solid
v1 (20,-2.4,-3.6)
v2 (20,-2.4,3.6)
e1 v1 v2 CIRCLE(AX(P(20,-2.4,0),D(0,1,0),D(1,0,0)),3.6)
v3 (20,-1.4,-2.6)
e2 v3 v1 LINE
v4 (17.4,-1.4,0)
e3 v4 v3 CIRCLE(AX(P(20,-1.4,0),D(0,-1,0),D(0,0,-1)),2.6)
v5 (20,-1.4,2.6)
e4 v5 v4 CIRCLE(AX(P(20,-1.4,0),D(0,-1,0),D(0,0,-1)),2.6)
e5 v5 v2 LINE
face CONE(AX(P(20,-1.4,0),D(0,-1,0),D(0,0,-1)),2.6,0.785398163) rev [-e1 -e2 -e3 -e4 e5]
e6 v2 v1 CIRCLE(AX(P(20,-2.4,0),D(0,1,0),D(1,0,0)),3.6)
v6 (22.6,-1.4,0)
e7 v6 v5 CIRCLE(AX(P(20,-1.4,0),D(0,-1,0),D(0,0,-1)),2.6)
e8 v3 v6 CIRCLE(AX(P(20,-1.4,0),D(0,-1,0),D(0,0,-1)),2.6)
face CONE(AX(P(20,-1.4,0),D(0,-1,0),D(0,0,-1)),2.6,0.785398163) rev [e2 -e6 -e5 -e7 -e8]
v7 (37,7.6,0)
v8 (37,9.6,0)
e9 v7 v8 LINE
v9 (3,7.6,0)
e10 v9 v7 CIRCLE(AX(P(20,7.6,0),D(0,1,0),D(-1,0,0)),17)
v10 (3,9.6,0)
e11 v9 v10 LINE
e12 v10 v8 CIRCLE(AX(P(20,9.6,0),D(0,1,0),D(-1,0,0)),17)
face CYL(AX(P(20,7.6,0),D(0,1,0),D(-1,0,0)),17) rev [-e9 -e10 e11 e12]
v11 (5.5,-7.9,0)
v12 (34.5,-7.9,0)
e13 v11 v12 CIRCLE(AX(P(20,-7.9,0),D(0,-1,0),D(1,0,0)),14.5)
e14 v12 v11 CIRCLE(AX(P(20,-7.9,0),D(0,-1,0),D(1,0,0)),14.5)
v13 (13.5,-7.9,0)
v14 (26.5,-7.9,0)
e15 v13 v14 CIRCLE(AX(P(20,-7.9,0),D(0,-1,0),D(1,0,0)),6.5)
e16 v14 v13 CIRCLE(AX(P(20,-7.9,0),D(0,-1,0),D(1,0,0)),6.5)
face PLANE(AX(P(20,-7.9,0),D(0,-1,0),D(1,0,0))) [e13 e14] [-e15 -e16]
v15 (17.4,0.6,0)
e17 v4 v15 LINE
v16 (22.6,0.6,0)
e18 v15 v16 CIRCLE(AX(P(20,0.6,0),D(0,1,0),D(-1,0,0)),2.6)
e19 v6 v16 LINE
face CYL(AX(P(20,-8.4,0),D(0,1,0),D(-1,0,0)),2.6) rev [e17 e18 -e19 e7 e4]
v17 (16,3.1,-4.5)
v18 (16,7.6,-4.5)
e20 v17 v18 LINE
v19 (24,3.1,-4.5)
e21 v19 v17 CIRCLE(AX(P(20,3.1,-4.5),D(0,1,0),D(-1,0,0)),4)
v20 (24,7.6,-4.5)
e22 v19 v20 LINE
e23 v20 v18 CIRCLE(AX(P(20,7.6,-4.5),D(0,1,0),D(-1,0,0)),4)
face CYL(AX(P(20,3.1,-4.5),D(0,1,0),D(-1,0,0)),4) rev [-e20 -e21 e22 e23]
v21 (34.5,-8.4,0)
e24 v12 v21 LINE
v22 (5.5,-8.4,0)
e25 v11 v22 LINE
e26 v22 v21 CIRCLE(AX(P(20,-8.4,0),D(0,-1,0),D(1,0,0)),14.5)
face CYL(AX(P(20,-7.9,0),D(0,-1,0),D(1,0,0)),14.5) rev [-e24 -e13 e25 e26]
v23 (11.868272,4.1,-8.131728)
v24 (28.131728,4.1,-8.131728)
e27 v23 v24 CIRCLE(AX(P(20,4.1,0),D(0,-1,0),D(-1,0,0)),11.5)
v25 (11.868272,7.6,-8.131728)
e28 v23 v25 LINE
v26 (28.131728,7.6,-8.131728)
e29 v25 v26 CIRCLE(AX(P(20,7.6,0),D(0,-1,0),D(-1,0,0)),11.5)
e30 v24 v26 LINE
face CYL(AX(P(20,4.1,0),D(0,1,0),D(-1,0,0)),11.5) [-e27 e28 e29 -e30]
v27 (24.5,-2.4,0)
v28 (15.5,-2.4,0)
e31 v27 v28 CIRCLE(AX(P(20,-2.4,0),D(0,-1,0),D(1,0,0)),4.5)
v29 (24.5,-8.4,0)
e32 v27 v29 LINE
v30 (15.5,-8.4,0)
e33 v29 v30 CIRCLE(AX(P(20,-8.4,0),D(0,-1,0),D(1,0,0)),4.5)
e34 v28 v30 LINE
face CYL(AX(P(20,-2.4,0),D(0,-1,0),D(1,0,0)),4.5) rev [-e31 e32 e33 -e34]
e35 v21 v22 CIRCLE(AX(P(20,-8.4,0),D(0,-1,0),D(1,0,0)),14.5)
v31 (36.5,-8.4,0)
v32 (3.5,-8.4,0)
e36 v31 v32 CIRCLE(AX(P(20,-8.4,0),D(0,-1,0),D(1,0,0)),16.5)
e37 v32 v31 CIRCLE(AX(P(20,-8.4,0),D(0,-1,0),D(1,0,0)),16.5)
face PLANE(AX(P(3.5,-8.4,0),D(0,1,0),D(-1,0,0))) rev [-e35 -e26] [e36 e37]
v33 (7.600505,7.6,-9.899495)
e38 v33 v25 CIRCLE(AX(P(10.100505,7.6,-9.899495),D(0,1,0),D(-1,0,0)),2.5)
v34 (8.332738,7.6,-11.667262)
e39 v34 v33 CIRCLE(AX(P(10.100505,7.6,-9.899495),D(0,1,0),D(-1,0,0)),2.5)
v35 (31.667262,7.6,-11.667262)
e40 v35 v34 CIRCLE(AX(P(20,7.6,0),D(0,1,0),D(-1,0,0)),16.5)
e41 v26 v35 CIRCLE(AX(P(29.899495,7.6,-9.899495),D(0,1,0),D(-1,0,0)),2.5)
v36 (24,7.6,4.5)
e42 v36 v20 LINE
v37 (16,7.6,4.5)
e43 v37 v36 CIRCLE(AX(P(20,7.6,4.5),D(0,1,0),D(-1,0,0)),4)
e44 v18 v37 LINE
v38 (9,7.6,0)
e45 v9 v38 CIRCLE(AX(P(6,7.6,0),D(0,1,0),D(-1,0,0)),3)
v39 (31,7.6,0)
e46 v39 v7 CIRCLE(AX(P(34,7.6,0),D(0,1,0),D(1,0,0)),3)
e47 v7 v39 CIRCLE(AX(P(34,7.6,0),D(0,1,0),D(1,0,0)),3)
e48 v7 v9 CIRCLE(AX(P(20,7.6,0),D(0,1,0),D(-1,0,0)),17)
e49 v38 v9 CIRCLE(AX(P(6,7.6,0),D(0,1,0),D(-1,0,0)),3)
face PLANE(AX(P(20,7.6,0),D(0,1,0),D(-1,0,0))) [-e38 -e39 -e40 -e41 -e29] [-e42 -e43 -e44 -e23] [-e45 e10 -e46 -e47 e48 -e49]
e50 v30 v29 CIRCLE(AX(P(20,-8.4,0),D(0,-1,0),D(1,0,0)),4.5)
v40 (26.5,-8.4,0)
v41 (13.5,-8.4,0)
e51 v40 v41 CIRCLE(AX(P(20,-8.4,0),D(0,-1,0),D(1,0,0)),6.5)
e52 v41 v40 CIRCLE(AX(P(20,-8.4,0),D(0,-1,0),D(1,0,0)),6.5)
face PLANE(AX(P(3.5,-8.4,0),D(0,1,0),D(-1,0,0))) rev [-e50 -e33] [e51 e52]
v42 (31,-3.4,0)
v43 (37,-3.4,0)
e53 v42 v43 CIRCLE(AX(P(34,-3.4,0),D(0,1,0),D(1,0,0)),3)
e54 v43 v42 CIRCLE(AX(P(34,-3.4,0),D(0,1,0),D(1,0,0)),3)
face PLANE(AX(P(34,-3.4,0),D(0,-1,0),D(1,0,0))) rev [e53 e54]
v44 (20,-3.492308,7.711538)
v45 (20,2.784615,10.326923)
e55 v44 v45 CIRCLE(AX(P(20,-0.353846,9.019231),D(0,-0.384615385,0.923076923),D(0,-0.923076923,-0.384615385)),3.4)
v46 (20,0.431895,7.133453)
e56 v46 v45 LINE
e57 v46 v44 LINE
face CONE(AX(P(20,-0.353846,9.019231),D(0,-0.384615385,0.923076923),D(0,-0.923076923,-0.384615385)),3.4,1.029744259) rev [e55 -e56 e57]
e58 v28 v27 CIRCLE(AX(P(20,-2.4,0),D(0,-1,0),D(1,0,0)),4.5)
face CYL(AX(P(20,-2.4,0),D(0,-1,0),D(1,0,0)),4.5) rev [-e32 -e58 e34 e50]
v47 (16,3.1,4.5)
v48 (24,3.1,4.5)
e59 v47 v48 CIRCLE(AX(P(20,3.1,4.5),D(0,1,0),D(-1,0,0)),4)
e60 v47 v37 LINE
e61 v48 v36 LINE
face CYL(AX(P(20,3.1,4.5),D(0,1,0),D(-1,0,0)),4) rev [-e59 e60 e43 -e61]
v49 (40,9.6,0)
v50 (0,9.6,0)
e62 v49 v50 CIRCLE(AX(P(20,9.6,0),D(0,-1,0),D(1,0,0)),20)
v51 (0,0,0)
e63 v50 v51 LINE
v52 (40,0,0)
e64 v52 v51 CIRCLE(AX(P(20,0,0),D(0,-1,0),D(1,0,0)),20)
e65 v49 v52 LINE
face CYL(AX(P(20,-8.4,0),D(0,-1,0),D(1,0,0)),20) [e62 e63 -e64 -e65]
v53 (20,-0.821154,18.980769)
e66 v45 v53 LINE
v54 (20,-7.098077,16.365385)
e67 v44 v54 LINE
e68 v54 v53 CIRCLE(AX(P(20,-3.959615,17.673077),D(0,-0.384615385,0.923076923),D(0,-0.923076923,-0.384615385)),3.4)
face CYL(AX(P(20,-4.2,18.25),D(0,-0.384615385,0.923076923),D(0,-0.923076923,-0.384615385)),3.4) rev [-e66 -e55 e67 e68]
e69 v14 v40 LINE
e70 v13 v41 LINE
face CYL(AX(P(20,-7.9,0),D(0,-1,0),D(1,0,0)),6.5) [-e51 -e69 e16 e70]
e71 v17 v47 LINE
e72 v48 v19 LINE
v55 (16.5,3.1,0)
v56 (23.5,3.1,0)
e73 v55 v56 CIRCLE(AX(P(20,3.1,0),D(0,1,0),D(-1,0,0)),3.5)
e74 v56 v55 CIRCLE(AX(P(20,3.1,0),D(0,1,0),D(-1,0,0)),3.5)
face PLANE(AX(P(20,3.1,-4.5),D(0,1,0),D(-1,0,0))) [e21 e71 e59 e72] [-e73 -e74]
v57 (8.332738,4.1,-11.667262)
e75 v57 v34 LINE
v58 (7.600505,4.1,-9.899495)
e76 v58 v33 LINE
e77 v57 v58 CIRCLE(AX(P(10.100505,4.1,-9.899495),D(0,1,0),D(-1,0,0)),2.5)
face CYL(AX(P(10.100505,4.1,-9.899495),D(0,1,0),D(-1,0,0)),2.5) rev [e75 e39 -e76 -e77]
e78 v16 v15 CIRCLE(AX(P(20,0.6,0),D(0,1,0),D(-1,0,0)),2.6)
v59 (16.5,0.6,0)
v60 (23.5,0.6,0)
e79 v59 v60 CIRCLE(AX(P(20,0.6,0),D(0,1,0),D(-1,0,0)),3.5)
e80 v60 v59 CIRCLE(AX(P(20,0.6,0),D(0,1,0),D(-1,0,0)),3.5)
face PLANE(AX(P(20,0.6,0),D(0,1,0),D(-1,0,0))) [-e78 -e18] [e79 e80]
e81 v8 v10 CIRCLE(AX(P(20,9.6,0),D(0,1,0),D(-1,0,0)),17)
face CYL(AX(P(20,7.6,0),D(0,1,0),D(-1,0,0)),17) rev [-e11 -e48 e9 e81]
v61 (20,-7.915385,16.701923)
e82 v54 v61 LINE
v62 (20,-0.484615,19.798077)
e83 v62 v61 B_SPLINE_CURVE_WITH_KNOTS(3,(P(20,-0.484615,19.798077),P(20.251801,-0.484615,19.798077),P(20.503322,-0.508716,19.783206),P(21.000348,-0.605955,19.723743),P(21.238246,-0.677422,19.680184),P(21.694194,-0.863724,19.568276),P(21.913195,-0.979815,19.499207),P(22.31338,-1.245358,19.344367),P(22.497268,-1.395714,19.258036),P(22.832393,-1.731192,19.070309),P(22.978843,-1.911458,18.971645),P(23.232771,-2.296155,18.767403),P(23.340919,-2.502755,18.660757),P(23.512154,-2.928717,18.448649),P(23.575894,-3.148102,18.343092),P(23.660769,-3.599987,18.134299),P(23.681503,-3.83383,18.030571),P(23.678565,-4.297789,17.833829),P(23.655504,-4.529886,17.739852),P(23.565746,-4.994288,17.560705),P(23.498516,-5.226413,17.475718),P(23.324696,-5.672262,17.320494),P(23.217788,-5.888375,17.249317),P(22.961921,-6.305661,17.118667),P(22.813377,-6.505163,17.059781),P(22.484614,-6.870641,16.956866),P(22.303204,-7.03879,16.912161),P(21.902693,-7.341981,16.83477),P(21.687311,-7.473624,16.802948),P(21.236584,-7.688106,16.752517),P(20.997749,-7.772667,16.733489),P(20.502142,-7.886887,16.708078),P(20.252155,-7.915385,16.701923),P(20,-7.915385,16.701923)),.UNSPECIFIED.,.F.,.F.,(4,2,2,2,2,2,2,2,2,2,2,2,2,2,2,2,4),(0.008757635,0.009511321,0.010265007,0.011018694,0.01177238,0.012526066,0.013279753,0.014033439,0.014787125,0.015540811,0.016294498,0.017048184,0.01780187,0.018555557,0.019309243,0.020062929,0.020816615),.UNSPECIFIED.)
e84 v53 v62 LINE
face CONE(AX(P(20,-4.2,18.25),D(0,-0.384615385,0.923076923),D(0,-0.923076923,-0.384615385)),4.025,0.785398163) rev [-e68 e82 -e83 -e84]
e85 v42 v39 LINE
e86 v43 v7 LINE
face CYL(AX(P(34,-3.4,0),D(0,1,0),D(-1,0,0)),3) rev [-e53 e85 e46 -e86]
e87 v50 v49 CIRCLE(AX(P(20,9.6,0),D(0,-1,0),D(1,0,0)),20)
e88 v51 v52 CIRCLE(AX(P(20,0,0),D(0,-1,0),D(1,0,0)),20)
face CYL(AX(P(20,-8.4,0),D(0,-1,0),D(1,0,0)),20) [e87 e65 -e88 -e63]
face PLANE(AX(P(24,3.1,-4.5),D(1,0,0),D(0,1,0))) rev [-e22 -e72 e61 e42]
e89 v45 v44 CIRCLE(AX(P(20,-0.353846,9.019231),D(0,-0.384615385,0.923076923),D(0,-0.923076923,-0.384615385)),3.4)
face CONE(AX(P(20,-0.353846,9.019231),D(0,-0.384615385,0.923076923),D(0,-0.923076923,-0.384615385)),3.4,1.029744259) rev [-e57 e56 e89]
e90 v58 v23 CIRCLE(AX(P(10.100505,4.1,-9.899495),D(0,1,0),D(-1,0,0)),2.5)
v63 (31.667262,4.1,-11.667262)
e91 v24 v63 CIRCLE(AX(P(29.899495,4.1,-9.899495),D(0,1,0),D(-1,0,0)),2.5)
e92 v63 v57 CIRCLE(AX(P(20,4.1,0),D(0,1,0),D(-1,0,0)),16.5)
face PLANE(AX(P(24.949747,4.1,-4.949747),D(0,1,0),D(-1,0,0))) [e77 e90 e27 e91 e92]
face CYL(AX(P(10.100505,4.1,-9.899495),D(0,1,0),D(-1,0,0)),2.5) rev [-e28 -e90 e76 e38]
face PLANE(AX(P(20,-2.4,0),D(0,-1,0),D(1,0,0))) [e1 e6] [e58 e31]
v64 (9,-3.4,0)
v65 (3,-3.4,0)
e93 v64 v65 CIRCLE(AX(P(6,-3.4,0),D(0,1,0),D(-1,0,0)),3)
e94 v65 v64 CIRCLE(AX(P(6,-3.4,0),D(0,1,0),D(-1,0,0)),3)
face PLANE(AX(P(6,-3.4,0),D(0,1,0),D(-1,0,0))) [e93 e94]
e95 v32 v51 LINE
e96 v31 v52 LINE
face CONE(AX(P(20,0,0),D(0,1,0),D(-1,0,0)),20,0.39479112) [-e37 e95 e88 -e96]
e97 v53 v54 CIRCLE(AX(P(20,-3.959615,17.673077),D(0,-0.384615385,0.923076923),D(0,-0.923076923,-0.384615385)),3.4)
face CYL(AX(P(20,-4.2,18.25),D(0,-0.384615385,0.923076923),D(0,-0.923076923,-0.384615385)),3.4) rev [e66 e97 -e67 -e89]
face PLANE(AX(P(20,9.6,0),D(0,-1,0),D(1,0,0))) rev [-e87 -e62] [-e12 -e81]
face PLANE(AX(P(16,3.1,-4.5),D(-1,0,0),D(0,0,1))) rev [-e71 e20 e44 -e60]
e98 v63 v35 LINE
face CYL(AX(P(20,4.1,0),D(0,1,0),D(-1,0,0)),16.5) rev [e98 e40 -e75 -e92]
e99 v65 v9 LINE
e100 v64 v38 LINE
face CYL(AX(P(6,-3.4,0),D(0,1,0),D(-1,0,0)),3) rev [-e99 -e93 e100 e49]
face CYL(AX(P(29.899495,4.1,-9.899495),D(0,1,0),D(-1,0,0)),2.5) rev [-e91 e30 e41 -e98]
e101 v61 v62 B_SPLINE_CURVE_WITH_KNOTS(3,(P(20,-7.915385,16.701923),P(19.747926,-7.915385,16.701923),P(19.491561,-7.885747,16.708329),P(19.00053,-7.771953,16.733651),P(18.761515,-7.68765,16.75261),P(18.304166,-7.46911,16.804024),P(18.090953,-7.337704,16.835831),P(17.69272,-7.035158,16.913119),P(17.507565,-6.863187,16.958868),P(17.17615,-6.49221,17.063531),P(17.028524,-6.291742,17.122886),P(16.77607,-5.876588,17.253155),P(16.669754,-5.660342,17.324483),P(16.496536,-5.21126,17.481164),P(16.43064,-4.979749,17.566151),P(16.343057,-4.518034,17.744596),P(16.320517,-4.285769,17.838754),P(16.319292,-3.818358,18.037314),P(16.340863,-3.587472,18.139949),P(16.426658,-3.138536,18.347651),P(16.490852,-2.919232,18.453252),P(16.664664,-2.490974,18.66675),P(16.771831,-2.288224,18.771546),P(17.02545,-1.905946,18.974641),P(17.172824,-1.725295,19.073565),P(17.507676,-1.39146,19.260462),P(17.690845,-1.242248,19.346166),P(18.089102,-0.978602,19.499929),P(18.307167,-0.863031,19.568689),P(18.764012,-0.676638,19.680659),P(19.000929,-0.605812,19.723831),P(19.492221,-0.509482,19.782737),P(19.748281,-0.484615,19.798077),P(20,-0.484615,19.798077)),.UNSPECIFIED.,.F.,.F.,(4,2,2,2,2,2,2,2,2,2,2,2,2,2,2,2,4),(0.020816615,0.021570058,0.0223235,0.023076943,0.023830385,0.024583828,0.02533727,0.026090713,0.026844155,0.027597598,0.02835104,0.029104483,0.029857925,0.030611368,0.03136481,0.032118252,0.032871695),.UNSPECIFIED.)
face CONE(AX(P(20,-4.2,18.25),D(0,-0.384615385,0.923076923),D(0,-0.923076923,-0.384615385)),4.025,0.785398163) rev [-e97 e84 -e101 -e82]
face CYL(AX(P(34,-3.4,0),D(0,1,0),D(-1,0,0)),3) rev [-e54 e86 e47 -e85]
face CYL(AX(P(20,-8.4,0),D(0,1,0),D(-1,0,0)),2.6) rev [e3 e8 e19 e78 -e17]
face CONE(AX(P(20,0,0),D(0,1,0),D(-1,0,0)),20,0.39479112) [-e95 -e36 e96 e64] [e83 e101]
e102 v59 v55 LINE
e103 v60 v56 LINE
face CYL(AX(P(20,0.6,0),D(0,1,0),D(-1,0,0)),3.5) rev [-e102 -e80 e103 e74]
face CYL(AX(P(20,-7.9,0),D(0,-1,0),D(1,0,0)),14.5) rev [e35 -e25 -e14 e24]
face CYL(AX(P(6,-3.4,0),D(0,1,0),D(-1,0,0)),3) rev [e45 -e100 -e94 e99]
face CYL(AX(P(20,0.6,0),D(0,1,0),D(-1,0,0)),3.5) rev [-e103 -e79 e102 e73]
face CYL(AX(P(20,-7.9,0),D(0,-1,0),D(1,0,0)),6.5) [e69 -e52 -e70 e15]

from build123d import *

# Parameters (mm, degrees)
SKETCH2_R                   = 17
CUT_EXTRUDE1_DEPTH          = 2
CUT_EXTRUDE2_DEPTH          = 4.5
CUT_EXTRUDE3_DEPTH          = 3.5
SKETCH5_R                   = 3
CUT_EXTRUDE4_DEPTH          = 11
SKETCH7_R                   = 4.5
CUT_EXTRUDE5_DEPTH          = 6
SKETCH8_R                   = 3.5
CUT_EXTRUDE6_DEPTH          = 2.5
SKETCH9_R                   = 2.6
CUT_EXTRUDE7_DEPTH          = 46.617978912
CHAMFER1_SIZE               = 1
SKETCH10_R                  = 14.5
SKETCH10_R_2                = 6.5
CUT_EXTRUDE8_DEPTH          = 0.5
M8_TAPPED_HOLE1_D           = 6.8
M8_TAPPED_HOLE1_DEPTH       = 10
M8_TAPPED_HOLE1_CSINK_D     = 8.05
M8_TAPPED_HOLE1_CSINK_ANGLE = 90
M8_TAPPED_HOLE1_TIP         = 2.042926105


with BuildPart() as part:
    # Sketch1 → Revolve1 (revolve)
    with BuildSketch(Plane.XY, mode=Mode.PRIVATE) as revolve1_sk:
        Polygon((0, 9.6), (0, 0), (3.5, -8.4), (20, -8.4), (20, 9.6), align=None)
    revolve(revolve1_sk.sketch.rotate(Axis((20, -8.4, 0), (0, 1, 0)), 180), axis=Axis((20, -8.4, 0), (0, 1, 0)))

    # Sketch2 → Cut-Extrude1 (cut)
    with BuildSketch(Plane(origin=(0, 9.6, 0), x_dir=(1, 0, 0), z_dir=(0, 1, 0))):
        with Locations(Location((20, 0, 0), (0, 0, 180))):
            Circle(SKETCH2_R)
    extrude(amount=-CUT_EXTRUDE1_DEPTH, mode=Mode.SUBTRACT)

    # Sketch3 → Cut-Extrude2 (cut)
    with BuildSketch(Plane(origin=(0, 7.6, 0), x_dir=(1, 0, 0), z_dir=(0, 1, 0))):
        with BuildLine():
            Line((24, 4.5), (24, -4.5))
            ThreePointArc((24, -4.5), (20, -8.5), (16, -4.5))
            Line((16, -4.5), (16, 4.5))
            ThreePointArc((16, 4.5), (20, 8.5), (24, 4.5))
        make_face()
    extrude(amount=-CUT_EXTRUDE2_DEPTH, mode=Mode.SUBTRACT)

    # Sketch4 → Cut-Extrude3 (cut)
    with BuildSketch(Plane(origin=(0, 7.6, 0), x_dir=(1, 0, 0), z_dir=(0, 1, 0))):
        with BuildLine():
            ThreePointArc((31.66726189, 11.66726189), (20, 16.5), (8.33273811, 11.66726189))
            ThreePointArc((8.33273811, 11.66726189), (8.33273811, 8.131727984), (11.868272016, 8.131727984))
            ThreePointArc((11.868272016, 8.131727984), (20, 11.5), (28.131727984, 8.131727984))
            ThreePointArc((28.131727984, 8.131727984), (31.66726189, 8.131727984), (31.66726189, 11.66726189))
        make_face()
    extrude(amount=-CUT_EXTRUDE3_DEPTH, mode=Mode.SUBTRACT)

    # Sketch5 → Cut-Extrude4 (cut)
    with BuildSketch(Plane(origin=(0, 7.6, 0), x_dir=(1, 0, 0), z_dir=(0, 1, 0))):
        with Locations(Location((6, 0, 0), (0, 0, 180))):
            Circle(SKETCH5_R)
        with Locations((34, 0)):
            Circle(SKETCH5_R)
    extrude(amount=-CUT_EXTRUDE4_DEPTH, mode=Mode.SUBTRACT)

    # Sketch7 → Cut-Extrude5 (cut)
    with BuildSketch(Plane.XZ.offset(8.4)):
        with Locations((20, 0)):
            Circle(SKETCH7_R)
    extrude(amount=-CUT_EXTRUDE5_DEPTH, mode=Mode.SUBTRACT)

    # Sketch8 → Cut-Extrude6 (cut)
    with BuildSketch(Plane(origin=(0, 3.1, 0), x_dir=(1, 0, 0), z_dir=(0, 1, 0))):
        with Locations(Location((20, 0, 0), (0, 0, 180))):
            Circle(SKETCH8_R)
    extrude(amount=-CUT_EXTRUDE6_DEPTH, mode=Mode.SUBTRACT)

    # Sketch9 → Cut-Extrude7 (cut, through all)
    with BuildSketch(Plane(origin=(0, 0.6, 0), x_dir=(1, 0, 0), z_dir=(0, 1, 0))):
        with Locations(Location((20, 0, 0), (0, 0, 180))):
            Circle(SKETCH9_R)
    extrude(amount=-CUT_EXTRUDE7_DEPTH, mode=Mode.SUBTRACT)

    # Chamfer1
    chamfer1_edges = [part.edges().sort_by_distance(p)[0] for p in [
        (22.6, -2.4, 0),
    ]]
    chamfer(chamfer1_edges, length=CHAMFER1_SIZE)

    # Sketch10 → Cut-Extrude8 (cut)
    with BuildSketch(Plane.XZ.offset(8.4)):
        with Locations((20, 0)):
            Circle(SKETCH10_R)
        with Locations((20, 0)):
            Circle(SKETCH10_R_2, mode=Mode.SUBTRACT)
    extrude(amount=-CUT_EXTRUDE8_DEPTH, mode=Mode.SUBTRACT)

    # M8 Tapped Hole1
    with Locations(Plane(origin=(0, -7.100591716, 17.041420118), x_dir=(1, 0, 0), z_dir=(0, -0.38461538461538547, 0.9230769230769227))):
        with Locations((20, 3.142307692)):
            CounterSinkHole(M8_TAPPED_HOLE1_D / 2, M8_TAPPED_HOLE1_CSINK_D / 2, depth=M8_TAPPED_HOLE1_DEPTH, counter_sink_angle=M8_TAPPED_HOLE1_CSINK_ANGLE)
            with Locations((0, 0, -(M8_TAPPED_HOLE1_DEPTH + M8_TAPPED_HOLE1_TIP / 2))):  # 118° drill point
                Cone(0, M8_TAPPED_HOLE1_D / 2, M8_TAPPED_HOLE1_TIP, mode=Mode.SUBTRACT)


solid = part.part
